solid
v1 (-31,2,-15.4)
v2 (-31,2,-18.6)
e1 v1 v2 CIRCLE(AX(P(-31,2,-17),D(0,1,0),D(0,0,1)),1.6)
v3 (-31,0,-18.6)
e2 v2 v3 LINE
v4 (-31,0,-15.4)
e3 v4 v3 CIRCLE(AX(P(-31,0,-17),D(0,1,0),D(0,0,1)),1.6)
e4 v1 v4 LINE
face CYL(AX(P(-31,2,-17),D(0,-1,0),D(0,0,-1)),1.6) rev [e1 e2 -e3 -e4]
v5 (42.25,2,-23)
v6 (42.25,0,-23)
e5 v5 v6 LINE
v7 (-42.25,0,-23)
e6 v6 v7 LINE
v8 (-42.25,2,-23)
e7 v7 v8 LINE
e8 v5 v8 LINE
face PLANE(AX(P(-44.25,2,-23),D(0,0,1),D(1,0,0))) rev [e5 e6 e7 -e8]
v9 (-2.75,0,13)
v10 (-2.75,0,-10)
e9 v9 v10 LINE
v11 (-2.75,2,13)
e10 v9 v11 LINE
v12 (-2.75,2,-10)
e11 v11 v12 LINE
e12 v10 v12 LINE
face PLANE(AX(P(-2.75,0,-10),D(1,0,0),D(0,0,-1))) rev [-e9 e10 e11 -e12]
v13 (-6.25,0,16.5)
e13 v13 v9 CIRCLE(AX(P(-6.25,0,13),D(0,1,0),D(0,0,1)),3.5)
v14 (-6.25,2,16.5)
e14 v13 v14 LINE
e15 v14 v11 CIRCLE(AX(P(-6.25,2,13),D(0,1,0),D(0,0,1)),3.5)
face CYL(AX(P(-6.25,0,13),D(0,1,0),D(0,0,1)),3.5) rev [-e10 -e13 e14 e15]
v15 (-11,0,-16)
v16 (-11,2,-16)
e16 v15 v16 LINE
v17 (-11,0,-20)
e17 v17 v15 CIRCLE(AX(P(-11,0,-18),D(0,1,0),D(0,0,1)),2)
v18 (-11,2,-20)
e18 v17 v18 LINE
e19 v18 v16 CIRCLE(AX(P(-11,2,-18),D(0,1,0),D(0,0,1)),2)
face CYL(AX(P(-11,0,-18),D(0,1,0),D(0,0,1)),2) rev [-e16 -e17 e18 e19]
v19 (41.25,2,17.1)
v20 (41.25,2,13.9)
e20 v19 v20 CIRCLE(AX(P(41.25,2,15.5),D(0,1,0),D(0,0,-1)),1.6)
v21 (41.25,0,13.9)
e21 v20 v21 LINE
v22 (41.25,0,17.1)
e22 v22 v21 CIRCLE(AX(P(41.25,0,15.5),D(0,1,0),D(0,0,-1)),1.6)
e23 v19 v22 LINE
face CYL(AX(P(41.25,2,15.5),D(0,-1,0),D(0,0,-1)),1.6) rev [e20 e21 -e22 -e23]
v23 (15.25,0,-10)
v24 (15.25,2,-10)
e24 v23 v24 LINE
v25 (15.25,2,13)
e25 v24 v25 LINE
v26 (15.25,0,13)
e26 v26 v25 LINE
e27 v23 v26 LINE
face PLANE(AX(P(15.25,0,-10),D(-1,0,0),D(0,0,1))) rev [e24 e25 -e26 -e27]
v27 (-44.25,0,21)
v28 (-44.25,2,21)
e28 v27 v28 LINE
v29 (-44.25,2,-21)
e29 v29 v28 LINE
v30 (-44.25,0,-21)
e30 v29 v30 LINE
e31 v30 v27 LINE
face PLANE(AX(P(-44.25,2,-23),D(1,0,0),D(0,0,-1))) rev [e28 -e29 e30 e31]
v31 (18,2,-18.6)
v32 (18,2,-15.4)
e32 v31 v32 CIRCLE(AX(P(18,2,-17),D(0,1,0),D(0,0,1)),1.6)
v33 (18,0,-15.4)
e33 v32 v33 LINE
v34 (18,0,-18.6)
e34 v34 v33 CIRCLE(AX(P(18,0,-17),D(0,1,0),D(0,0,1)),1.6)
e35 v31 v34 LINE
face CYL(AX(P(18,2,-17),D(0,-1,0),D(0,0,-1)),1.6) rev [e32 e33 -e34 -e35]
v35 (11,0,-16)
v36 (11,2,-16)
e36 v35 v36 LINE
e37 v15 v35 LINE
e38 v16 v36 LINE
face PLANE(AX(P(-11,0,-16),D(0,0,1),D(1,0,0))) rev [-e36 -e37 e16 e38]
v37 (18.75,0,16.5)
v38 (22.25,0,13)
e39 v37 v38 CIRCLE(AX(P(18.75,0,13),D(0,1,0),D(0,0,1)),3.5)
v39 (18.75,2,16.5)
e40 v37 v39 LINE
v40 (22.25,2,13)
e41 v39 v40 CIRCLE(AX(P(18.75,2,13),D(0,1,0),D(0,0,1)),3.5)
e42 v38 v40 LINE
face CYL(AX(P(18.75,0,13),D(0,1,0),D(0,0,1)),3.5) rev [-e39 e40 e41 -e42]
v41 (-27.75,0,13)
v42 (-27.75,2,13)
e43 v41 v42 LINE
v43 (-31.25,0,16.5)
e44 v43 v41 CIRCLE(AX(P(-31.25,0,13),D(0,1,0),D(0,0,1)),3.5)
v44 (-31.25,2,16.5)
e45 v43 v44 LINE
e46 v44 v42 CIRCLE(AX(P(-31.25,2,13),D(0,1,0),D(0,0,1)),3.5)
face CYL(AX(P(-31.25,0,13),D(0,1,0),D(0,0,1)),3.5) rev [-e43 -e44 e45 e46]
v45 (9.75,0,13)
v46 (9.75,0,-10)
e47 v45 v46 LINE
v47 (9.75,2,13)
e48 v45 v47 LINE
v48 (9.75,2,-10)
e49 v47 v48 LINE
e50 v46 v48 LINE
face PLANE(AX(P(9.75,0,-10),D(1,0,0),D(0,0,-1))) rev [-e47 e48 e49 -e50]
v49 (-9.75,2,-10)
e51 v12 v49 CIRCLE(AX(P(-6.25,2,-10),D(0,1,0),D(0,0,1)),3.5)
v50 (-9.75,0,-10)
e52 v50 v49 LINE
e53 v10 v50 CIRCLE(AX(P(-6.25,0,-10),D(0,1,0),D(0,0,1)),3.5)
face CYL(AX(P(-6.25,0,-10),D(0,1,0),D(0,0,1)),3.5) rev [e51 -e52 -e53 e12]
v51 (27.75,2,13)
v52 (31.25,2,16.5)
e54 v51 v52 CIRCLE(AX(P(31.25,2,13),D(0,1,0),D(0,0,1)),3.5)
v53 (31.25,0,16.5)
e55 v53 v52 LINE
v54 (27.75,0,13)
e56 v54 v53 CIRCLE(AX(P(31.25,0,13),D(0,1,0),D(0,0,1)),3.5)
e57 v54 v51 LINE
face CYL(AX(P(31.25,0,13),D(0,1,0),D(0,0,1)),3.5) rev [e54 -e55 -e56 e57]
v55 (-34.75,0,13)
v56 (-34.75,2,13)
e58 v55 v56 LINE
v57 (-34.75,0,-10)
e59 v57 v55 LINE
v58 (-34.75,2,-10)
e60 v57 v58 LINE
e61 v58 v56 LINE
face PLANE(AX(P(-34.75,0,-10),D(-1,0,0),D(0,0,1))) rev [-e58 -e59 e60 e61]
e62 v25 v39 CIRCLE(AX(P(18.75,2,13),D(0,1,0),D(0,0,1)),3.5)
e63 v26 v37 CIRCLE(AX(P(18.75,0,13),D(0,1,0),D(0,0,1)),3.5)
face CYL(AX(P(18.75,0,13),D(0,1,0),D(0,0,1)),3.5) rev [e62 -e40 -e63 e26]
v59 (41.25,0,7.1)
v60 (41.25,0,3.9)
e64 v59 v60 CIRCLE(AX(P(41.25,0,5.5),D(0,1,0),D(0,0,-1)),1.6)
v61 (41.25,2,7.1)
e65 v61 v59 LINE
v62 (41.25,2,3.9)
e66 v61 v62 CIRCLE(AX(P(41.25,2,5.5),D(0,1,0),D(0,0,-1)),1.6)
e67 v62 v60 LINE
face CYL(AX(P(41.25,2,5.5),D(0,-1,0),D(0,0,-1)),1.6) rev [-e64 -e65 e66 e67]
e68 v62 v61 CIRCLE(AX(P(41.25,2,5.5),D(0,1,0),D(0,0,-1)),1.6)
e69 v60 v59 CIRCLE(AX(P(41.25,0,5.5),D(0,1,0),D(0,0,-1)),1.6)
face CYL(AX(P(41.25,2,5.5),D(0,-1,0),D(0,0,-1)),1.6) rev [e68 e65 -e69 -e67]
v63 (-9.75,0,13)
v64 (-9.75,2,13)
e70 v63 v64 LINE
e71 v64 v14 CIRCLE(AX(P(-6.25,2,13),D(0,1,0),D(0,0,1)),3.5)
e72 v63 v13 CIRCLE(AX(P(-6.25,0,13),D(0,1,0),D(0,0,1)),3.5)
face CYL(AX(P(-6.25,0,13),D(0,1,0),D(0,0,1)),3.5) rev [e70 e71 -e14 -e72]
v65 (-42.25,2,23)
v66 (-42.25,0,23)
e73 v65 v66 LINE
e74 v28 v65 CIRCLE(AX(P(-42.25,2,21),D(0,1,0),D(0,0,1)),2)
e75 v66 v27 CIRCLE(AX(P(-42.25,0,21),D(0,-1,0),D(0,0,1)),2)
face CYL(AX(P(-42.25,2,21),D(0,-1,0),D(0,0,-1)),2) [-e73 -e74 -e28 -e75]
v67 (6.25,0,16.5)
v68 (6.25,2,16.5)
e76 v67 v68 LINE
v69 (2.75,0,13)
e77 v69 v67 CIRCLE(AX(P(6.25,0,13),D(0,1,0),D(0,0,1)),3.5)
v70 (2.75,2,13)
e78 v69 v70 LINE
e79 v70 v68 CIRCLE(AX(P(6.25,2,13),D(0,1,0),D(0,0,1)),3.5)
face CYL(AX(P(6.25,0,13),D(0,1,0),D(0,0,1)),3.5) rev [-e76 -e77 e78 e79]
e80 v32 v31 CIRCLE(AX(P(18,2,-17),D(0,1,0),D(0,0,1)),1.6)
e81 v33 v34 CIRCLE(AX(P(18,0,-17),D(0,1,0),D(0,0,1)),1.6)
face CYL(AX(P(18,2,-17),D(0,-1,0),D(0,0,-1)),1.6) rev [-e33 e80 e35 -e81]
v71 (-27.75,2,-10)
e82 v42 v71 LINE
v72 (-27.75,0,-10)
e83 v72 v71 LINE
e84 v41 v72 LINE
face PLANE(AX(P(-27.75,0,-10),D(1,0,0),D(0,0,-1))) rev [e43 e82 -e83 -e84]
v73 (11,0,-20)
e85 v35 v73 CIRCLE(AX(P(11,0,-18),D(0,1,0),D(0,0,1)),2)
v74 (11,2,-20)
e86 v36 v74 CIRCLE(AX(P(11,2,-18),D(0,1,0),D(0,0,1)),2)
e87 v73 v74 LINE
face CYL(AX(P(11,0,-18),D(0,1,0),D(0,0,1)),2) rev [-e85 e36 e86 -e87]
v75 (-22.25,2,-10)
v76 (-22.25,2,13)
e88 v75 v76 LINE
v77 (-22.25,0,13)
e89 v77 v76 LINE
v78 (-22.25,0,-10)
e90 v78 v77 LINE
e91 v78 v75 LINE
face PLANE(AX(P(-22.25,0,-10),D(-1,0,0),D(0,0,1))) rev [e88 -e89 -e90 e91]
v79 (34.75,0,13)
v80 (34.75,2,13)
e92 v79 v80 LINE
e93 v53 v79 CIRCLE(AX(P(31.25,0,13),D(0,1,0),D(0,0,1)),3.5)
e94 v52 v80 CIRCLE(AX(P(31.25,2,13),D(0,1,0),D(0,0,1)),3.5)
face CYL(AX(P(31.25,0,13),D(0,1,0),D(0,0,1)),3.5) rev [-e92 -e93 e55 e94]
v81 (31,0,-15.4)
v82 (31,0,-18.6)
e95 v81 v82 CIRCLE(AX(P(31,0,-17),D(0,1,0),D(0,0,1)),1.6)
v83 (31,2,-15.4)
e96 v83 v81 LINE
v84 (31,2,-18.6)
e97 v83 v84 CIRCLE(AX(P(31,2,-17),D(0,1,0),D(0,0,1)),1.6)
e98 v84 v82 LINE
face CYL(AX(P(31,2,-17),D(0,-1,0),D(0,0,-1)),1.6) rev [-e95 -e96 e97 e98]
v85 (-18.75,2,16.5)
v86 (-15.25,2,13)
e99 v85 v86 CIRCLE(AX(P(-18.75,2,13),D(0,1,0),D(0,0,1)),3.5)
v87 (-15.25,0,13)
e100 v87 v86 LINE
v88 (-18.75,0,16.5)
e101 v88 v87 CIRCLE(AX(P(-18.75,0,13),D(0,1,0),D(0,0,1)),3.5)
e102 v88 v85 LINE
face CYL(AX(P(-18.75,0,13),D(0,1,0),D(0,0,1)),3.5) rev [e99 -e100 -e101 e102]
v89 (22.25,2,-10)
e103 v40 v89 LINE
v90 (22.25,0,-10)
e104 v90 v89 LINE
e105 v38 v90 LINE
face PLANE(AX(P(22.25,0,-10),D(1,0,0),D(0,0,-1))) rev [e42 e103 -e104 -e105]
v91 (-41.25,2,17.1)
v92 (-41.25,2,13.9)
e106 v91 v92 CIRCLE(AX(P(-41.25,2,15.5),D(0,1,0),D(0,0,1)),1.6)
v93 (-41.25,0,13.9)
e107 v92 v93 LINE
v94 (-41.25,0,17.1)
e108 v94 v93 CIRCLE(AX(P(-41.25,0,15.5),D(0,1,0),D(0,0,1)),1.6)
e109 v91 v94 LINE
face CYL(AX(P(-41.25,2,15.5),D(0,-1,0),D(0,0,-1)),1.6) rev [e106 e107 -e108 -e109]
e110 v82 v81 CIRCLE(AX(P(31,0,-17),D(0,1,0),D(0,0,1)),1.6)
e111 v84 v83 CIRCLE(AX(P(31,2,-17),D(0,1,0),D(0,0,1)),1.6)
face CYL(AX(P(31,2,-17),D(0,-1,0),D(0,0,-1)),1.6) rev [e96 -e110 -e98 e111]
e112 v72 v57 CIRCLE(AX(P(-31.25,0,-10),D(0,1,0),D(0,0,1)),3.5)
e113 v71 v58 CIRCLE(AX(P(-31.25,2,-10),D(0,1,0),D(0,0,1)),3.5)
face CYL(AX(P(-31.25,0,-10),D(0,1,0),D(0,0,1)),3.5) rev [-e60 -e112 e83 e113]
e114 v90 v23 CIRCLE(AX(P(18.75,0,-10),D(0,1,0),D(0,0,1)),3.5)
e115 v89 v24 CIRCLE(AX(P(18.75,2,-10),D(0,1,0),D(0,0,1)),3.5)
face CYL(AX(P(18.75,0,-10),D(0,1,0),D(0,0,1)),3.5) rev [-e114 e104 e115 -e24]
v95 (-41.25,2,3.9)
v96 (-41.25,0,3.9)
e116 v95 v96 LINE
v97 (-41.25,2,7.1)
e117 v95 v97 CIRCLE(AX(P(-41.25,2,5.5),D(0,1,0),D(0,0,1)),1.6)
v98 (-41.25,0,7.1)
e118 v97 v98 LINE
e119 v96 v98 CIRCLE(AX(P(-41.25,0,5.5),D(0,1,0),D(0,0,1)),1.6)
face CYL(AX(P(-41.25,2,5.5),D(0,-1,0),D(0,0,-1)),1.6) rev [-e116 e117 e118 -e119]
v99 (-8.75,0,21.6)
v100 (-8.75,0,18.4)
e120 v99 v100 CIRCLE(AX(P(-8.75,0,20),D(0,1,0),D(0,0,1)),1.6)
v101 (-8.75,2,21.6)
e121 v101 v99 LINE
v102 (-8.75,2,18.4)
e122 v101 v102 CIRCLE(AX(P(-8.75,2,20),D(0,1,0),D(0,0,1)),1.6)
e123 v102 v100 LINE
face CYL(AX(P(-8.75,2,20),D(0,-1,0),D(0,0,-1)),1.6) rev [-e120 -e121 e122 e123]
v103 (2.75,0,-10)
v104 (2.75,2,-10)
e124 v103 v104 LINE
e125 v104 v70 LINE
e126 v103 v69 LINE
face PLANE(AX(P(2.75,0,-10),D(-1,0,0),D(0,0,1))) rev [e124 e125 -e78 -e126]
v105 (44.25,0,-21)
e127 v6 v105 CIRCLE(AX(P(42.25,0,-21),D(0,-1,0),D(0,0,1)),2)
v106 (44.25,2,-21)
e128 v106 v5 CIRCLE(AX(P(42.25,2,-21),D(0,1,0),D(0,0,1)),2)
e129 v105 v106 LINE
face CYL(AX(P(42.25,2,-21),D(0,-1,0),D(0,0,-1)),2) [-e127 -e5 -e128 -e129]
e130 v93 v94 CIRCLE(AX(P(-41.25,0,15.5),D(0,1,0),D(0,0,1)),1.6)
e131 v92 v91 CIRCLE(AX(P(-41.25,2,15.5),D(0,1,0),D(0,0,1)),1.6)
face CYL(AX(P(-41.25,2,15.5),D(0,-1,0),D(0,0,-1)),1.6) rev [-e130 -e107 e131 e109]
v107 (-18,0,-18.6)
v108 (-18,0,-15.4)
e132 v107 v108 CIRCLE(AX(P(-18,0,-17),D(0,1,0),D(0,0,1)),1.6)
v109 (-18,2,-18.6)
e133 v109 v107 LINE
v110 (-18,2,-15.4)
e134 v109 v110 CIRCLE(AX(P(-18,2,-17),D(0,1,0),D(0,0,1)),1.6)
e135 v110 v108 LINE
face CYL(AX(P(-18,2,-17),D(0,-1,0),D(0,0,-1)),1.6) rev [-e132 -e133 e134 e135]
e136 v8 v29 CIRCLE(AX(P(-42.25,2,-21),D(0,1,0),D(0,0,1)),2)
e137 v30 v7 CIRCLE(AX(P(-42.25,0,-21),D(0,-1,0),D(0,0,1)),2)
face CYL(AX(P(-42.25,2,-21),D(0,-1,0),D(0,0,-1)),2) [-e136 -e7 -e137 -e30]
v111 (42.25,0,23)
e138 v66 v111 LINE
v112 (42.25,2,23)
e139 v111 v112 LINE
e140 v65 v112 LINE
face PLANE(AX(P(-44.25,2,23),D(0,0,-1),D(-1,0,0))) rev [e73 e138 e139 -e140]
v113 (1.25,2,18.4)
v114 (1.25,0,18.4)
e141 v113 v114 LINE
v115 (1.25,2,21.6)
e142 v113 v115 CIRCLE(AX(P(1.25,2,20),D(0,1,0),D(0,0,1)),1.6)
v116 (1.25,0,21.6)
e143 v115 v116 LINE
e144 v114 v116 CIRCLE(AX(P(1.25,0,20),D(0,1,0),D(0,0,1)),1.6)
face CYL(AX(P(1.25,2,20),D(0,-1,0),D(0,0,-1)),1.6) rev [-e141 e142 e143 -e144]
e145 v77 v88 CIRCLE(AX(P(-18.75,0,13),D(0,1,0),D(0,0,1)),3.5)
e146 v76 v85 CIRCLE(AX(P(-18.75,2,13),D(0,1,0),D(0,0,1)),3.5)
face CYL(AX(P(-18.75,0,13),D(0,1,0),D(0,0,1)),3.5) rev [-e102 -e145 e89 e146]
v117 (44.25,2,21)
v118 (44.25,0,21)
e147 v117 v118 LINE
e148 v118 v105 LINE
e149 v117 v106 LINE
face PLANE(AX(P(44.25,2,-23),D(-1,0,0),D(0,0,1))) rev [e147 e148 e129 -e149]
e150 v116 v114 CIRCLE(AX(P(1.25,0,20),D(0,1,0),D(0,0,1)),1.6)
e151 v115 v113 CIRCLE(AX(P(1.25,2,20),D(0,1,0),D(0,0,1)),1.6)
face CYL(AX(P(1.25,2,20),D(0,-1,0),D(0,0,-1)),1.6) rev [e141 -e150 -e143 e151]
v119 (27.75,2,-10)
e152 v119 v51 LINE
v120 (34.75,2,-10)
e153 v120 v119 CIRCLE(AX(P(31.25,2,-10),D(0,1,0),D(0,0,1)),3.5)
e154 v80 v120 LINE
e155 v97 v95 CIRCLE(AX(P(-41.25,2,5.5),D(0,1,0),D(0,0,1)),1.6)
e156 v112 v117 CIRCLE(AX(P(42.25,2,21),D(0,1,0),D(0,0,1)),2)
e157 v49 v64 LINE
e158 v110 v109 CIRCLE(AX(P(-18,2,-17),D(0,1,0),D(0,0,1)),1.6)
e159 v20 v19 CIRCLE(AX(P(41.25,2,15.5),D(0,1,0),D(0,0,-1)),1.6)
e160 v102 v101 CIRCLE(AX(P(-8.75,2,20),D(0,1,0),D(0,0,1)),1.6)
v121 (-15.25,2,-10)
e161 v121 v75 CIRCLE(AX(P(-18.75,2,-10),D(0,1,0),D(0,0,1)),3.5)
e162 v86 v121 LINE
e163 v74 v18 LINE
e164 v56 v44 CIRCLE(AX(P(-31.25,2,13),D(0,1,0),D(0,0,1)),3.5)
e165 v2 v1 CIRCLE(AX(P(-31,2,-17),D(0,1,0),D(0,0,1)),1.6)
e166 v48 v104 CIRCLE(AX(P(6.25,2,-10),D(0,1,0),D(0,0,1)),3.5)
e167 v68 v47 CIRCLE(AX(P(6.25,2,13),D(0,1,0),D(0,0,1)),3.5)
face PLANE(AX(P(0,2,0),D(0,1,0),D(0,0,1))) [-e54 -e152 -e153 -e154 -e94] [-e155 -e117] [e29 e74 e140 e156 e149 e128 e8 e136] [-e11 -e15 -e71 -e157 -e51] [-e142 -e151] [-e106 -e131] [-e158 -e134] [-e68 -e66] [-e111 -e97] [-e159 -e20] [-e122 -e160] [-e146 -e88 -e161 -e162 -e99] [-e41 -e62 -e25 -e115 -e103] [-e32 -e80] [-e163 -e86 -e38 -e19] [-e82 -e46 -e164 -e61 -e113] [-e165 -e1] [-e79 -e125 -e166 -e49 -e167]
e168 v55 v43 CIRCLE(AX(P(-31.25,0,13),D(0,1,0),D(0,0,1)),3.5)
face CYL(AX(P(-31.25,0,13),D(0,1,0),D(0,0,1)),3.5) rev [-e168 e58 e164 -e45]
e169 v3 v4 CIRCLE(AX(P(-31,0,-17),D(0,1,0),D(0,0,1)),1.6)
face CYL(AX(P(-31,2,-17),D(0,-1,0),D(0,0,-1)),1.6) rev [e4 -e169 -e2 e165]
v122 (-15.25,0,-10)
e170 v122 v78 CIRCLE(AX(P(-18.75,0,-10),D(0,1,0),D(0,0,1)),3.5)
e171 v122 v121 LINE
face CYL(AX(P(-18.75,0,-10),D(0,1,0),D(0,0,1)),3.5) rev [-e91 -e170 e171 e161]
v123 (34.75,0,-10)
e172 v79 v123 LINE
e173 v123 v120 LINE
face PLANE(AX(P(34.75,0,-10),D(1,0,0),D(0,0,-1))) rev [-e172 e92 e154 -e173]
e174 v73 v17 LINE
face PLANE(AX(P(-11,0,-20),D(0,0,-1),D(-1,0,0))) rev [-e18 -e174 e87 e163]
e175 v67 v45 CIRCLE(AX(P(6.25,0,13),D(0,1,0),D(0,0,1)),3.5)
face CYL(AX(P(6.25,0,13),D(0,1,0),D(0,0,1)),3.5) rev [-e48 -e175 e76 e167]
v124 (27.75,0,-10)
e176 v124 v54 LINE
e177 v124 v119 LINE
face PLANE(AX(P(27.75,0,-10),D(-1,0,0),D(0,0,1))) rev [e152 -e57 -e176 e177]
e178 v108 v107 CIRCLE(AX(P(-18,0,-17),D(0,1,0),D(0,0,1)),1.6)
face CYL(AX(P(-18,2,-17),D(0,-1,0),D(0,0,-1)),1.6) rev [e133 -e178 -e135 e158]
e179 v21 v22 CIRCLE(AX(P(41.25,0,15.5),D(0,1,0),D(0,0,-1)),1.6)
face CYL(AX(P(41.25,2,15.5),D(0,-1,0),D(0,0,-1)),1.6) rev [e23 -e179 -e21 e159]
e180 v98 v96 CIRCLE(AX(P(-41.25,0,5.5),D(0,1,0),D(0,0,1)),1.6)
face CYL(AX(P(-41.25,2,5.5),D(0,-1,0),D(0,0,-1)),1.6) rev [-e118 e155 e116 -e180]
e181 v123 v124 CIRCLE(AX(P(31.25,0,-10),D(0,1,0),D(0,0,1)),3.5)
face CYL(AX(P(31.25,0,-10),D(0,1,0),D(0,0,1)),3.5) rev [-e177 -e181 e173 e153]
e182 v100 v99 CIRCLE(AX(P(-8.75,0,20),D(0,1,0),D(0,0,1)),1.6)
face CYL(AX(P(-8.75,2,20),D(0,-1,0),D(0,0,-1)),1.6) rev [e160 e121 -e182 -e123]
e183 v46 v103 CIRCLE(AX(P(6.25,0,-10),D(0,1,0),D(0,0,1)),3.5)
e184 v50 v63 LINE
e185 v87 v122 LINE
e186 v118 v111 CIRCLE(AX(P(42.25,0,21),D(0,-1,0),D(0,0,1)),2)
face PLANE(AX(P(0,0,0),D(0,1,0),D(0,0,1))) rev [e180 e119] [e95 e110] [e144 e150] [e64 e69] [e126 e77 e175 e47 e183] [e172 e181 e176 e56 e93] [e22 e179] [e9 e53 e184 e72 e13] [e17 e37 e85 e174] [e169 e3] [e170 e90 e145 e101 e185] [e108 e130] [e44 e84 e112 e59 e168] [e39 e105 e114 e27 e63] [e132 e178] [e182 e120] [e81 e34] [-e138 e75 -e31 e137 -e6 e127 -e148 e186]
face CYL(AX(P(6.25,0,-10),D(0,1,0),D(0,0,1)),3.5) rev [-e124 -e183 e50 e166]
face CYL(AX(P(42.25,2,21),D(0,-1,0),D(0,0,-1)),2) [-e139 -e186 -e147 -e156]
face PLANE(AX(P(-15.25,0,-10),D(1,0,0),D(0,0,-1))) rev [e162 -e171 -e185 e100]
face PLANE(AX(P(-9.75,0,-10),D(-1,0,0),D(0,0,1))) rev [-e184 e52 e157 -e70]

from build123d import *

# Parameters (mm, degrees)
SKETCH1_W           = 88.5
SKETCH1_H           = 46
SKETCH1_R           = 1.6
BOSS_EXTRUDE1_DEPTH = 2
CUT_EXTRUDE1_DEPTH  = 50.910544978
FILLET1_R           = 2


with BuildPart() as part:
    # Sketch1 → Boss-Extrude1 (new body)
    with BuildSketch(Plane(origin=(0, 0, 0), x_dir=(1, 0, 0), z_dir=(0, 1, 0))):
        Rectangle(SKETCH1_W, SKETCH1_H)
        with Locations(Location((-41.25, -5.5, 0), (0, 0, 270))):
            Circle(SKETCH1_R, mode=Mode.SUBTRACT)
        with Locations(Location((-41.25, -15.5, 0), (0, 0, 270))):
            Circle(SKETCH1_R, mode=Mode.SUBTRACT)
        with Locations(Location((41.25, -15.5, 0), (0, 0, 90))):
            Circle(SKETCH1_R, mode=Mode.SUBTRACT)
        with Locations(Location((41.25, -5.5, 0), (0, 0, 90))):
            Circle(SKETCH1_R, mode=Mode.SUBTRACT)
        with Locations(Location((-8.75, -20, 0), (0, 0, 270))):
            Circle(SKETCH1_R, mode=Mode.SUBTRACT)
        with Locations(Location((1.25, -20, 0), (0, 0, 270))):
            Circle(SKETCH1_R, mode=Mode.SUBTRACT)
        with Locations(Location((-31, 17, 0), (0, 0, 270))):
            Circle(SKETCH1_R, mode=Mode.SUBTRACT)
        with Locations(Location((-18, 17, 0), (0, 0, 270))):
            Circle(SKETCH1_R, mode=Mode.SUBTRACT)
        with Locations(Location((18, 17, 0), (0, 0, 270))):
            Circle(SKETCH1_R, mode=Mode.SUBTRACT)
        with Locations(Location((31, 17, 0), (0, 0, 270))):
            Circle(SKETCH1_R, mode=Mode.SUBTRACT)
    extrude(amount=BOSS_EXTRUDE1_DEPTH)

    # Sketch2 → Cut-Extrude1 (cut, through all)
    with BuildSketch(Plane(origin=(0, 2, 0), x_dir=(1, 0, 0), z_dir=(0, 1, 0))):
        with BuildLine():
            Line((-27.75, 10), (-27.75, -13))
            ThreePointArc((-27.75, -13), (-31.25, -16.5), (-34.75, -13))
            Line((-34.75, -13), (-34.75, 10))
            ThreePointArc((-34.75, 10), (-31.25, 13.5), (-27.75, 10))
        make_face()
        with BuildLine():
            Line((-15.25, 10), (-15.25, -13))
            ThreePointArc((-15.25, -13), (-18.75, -16.5), (-22.25, -13))
            Line((-22.25, -13), (-22.25, 10))
            ThreePointArc((-22.25, 10), (-18.75, 13.5), (-15.25, 10))
        make_face()
        with BuildLine():
            Line((-2.75, 10), (-2.75, -13))
            ThreePointArc((-2.75, -13), (-6.25, -16.5), (-9.75, -13))
            Line((-9.75, -13), (-9.75, 10))
            ThreePointArc((-9.75, 10), (-6.25, 13.5), (-2.75, 10))
        make_face()
        with BuildLine():
            Line((9.75, 10), (9.75, -13))
            ThreePointArc((9.75, -13), (6.25, -16.5), (2.75, -13))
            Line((2.75, -13), (2.75, 10))
            ThreePointArc((2.75, 10), (6.25, 13.5), (9.75, 10))
        make_face()
        with BuildLine():
            Line((22.25, 10), (22.25, -13))
            ThreePointArc((22.25, -13), (18.75, -16.5), (15.25, -13))
            Line((15.25, -13), (15.25, 10))
            ThreePointArc((15.25, 10), (18.75, 13.5), (22.25, 10))
        make_face()
        with BuildLine():
            Line((34.75, 10), (34.75, -13))
            ThreePointArc((34.75, -13), (31.25, -16.5), (27.75, -13))
            Line((27.75, -13), (27.75, 10))
            ThreePointArc((27.75, 10), (31.25, 13.5), (34.75, 10))
        make_face()
        with BuildLine():
            Line((-11, 20), (11, 20))
            ThreePointArc((11, 20), (13, 18), (11, 16))
            Line((11, 16), (-11, 16))
            ThreePointArc((-11, 16), (-13, 18), (-11, 20))
        make_face()
    extrude(amount=-CUT_EXTRUDE1_DEPTH, mode=Mode.SUBTRACT)

    # Fillet1
    fillet1_edges = [part.edges().sort_by_distance(p)[0] for p in [
        (44.25, 1, 23),
        (-44.25, 1, 23),
        (-44.25, 1, -23),
        (44.25, 1, -23),
    ]]
    fillet(fillet1_edges, radius=FILLET1_R)


solid = part.part
